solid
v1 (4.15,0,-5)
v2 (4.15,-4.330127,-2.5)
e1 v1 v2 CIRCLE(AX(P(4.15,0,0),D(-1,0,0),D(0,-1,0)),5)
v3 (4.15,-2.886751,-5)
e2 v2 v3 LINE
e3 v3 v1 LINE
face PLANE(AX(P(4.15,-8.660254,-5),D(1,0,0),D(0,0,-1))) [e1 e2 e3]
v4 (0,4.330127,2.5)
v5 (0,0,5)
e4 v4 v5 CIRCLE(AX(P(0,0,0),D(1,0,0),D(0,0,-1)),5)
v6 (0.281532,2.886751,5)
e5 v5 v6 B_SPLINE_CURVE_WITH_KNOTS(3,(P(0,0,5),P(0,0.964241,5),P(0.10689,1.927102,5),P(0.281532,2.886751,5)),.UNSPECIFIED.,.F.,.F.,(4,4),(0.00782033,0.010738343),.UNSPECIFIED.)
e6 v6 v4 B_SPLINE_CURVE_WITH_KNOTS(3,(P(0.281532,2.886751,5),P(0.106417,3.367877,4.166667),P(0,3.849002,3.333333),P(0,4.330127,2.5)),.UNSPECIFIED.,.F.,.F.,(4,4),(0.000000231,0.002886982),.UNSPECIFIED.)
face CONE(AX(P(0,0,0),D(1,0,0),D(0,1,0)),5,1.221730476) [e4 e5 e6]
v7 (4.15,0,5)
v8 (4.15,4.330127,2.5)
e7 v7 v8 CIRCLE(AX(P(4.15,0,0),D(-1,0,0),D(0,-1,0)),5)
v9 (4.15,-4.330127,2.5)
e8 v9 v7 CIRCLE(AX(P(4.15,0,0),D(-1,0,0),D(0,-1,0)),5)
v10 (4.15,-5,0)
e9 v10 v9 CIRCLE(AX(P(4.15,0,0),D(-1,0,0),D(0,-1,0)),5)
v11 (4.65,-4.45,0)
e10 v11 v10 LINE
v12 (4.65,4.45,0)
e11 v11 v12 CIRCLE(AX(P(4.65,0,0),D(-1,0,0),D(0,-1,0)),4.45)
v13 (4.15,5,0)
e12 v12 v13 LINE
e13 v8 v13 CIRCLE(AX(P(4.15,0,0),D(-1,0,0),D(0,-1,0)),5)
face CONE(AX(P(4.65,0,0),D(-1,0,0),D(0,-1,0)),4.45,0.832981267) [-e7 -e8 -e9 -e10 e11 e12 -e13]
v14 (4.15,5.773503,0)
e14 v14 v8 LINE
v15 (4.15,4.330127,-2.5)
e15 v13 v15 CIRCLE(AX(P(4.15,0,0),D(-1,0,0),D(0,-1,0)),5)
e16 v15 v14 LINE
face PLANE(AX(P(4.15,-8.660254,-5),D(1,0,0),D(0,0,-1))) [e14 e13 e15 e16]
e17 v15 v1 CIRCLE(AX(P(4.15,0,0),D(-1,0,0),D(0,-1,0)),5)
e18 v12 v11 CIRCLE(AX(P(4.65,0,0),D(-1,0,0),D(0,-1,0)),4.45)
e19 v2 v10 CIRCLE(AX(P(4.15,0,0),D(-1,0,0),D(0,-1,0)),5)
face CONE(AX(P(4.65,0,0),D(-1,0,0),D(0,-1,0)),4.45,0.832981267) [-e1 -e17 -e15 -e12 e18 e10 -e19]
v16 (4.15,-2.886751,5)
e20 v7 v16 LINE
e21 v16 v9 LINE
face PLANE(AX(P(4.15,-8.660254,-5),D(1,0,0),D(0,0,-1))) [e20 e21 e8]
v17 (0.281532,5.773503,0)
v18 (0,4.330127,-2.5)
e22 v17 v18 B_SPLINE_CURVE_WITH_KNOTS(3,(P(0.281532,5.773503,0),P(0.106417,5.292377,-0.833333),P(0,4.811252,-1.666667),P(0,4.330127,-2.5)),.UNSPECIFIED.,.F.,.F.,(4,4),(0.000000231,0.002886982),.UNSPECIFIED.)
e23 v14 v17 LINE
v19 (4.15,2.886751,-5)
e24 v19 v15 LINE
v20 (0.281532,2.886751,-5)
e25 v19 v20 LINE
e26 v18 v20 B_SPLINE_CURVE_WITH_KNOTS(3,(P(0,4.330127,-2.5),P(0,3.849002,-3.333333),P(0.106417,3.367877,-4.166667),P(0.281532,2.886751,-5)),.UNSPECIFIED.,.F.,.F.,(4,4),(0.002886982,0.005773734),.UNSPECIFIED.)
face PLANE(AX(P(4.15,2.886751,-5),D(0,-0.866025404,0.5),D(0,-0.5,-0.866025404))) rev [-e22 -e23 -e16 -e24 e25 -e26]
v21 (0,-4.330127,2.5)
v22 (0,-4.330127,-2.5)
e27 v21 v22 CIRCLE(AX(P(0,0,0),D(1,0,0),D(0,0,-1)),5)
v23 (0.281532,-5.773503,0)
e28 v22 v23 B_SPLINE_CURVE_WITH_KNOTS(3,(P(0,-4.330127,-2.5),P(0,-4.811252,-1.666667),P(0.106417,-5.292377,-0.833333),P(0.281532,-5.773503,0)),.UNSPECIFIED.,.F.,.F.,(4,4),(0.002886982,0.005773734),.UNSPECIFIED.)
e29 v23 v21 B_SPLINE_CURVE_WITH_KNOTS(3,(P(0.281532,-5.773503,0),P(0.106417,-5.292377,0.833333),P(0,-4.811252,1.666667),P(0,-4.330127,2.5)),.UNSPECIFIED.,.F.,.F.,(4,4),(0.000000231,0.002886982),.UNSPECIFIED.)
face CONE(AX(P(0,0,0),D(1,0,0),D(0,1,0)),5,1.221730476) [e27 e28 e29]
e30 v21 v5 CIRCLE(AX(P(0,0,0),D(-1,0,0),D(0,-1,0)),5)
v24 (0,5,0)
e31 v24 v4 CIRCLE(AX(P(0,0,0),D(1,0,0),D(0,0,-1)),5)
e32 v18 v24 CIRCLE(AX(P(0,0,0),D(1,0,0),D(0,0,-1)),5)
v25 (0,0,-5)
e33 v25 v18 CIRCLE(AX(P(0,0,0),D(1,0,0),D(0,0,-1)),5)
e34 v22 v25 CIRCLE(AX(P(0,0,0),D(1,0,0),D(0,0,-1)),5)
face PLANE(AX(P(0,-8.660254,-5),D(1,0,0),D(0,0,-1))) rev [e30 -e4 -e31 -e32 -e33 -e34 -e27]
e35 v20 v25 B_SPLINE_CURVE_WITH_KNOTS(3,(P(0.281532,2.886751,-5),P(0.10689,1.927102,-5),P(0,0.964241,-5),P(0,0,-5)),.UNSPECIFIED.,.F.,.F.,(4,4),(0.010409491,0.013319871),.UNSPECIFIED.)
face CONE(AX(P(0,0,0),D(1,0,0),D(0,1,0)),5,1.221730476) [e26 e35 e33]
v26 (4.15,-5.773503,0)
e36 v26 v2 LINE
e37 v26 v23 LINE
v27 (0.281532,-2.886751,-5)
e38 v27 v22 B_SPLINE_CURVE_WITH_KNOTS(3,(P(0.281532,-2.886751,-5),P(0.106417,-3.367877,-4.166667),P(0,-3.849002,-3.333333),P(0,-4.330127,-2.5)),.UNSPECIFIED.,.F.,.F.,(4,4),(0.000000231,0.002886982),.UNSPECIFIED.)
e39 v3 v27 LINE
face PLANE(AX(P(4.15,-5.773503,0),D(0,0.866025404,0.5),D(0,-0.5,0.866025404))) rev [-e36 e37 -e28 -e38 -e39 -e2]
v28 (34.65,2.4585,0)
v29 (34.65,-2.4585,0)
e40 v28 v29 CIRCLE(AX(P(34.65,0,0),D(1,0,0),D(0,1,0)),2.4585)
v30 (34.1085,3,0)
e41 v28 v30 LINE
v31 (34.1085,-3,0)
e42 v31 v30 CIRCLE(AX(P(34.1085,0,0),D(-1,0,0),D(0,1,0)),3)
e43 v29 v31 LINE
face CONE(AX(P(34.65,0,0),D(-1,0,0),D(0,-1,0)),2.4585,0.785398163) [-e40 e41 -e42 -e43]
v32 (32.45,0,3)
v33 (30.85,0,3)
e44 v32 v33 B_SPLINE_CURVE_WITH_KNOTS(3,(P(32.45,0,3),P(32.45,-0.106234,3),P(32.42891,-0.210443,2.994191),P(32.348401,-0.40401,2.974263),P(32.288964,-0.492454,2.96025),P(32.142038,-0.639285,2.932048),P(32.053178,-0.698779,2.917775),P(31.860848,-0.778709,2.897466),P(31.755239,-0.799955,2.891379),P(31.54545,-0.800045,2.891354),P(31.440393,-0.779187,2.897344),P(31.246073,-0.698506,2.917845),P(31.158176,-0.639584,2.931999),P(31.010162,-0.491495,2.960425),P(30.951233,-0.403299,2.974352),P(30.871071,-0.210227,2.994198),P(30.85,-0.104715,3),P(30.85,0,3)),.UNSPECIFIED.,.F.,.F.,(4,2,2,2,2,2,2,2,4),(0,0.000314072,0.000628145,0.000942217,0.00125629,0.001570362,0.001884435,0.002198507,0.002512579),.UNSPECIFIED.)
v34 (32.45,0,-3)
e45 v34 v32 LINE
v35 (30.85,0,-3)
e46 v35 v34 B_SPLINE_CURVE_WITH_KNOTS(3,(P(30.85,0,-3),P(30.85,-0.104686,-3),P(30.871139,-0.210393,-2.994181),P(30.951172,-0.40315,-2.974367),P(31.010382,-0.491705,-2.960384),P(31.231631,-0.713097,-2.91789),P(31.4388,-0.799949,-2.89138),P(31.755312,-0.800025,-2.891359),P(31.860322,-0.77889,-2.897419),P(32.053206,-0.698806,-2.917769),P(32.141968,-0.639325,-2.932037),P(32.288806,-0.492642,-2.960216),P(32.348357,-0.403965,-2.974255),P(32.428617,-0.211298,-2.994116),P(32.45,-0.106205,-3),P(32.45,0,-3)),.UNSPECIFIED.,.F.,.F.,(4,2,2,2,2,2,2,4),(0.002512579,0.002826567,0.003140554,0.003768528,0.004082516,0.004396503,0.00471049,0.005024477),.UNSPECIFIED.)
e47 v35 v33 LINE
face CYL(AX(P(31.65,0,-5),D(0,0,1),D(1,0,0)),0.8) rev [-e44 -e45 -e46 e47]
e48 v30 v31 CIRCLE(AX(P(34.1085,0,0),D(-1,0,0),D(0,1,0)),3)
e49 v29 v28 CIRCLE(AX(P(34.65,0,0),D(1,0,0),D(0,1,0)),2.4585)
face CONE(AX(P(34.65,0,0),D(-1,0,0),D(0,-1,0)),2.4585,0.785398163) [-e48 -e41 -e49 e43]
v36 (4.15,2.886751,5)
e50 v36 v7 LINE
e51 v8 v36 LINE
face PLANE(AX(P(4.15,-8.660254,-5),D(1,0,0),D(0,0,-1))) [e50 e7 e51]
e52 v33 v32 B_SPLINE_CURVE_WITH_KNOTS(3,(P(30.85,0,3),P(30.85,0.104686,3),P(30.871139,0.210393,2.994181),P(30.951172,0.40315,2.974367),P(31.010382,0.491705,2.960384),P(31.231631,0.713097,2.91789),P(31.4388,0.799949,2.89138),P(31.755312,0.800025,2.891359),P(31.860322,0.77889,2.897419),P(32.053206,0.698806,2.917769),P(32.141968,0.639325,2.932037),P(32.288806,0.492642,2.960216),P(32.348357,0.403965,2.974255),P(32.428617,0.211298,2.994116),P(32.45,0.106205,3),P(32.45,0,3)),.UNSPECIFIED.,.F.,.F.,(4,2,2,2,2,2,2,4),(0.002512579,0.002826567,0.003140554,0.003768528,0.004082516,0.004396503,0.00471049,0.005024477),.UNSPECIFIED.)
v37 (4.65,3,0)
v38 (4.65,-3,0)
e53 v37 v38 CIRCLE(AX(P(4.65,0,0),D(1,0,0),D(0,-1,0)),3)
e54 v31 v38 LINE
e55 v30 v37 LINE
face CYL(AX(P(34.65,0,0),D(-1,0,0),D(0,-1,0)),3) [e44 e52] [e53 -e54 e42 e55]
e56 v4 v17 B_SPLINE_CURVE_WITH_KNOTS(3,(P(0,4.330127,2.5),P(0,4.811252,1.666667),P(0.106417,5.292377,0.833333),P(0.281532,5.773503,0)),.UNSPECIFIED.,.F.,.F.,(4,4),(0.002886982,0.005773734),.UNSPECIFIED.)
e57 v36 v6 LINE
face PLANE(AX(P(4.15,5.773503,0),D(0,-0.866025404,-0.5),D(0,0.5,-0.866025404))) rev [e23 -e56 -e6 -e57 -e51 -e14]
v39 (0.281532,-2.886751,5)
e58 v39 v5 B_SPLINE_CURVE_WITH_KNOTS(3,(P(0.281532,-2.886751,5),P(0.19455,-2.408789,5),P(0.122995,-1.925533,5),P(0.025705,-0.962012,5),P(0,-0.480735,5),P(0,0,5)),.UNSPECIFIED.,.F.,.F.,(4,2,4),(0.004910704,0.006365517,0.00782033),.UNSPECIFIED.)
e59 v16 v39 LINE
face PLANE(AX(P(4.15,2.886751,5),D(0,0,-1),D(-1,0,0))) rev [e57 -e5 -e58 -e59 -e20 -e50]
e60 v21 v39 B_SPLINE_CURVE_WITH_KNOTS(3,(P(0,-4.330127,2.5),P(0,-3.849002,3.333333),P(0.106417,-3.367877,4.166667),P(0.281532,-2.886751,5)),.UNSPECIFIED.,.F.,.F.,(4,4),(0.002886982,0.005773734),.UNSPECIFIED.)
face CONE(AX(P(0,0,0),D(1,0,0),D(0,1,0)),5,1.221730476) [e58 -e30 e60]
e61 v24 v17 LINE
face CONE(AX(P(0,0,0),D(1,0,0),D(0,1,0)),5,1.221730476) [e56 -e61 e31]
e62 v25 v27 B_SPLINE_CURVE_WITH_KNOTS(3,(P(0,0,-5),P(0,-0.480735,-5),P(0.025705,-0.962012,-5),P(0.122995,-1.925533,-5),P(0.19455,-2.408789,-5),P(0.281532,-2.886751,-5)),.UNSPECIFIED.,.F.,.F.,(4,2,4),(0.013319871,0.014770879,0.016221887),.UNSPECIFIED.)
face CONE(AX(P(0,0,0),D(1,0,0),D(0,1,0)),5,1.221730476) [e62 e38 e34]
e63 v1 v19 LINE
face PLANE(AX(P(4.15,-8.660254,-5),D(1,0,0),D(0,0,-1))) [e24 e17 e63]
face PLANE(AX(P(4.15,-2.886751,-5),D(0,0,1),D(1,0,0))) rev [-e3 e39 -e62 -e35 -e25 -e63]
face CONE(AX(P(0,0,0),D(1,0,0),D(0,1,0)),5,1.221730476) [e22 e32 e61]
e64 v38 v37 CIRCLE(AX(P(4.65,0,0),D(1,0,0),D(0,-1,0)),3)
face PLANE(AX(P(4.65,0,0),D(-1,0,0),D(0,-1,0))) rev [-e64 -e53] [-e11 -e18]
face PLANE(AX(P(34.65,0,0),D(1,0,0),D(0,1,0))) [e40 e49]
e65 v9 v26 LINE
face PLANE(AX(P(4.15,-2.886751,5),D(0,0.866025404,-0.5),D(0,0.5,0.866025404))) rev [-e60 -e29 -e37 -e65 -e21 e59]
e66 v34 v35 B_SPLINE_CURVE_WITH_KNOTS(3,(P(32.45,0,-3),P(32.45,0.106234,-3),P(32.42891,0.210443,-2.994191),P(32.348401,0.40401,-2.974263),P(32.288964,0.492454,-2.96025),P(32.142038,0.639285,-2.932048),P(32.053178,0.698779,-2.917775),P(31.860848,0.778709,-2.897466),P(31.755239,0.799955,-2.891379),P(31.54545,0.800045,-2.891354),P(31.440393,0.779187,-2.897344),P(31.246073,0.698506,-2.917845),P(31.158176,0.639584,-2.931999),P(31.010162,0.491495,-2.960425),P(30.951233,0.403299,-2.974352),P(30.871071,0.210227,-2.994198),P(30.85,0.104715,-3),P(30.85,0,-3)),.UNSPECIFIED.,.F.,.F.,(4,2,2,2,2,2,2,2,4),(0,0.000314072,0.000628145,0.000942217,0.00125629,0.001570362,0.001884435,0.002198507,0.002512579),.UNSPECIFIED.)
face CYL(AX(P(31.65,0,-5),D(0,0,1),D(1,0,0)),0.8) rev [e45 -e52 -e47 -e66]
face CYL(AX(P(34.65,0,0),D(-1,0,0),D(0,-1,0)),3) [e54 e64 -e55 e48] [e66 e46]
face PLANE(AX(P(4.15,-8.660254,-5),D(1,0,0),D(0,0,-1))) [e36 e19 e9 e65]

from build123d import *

# Parameters (mm, degrees)
BASEHEAD_DEPTH  = 4.15
SKETCH3_R       = 3
BASEBODY_DEPTH  = 30
CHAMFER1_SIZE   = 0.5415
HOLE_DEPTH      = 36.481767619
HOLE_DEPTH_BACK = 36.481767619
SKETCH5_R       = 0.8


with BuildPart() as part:
    # Sketch-BaseHead → BaseHead (new body)
    with BuildSketch(Plane(origin=(0, 0, 0), x_dir=(0, 0, -1), z_dir=(1, 0, 0))):
        Polygon((0, -5.773502692), (5, -2.886751346), (5, 2.886751346), (0, 5.773502692), (-5, 2.886751346), (-5, -2.886751346), align=None)
    extrude(amount=BASEHEAD_DEPTH)

    # Sketch4 → HeadChamfer (revolve, cut)
    with BuildSketch(Plane(origin=(-0.264637255, -5.916896391, 0), x_dir=(0, 1, 0), z_dir=(0, 0, 1))):
        Polygon((11.690399083, -0.264637255), (10.916896391, -0.264637255), (11.690399083, -0.546169211), align=None)
    revolve(axis=Axis((-4.001564945, 0, 0), (1, 0, 0)), mode=Mode.SUBTRACT)

    # Sketch1 → Revolve1 (revolve)
    with BuildSketch(Plane(origin=(0, 0, 0), x_dir=(1, 0, 0), z_dir=(0, 1, 0)), mode=Mode.PRIVATE) as revolve1_sk:
        Polygon((4.15, 0), (4.65, 0), (4.65, 4.45), (4.15, 5), align=None)
    revolve(revolve1_sk.sketch.rotate(Axis((-4.001564945, 0, 0), (1, 0, 0)), 270), axis=Axis((-4.001564945, 0, 0), (1, 0, 0)))

    # Sketch3 → BaseBody (add)
    with BuildSketch(Plane(origin=(4.65, 0, 0), x_dir=(0, 0, -1), z_dir=(1, 0, 0))):
        with Locations(Location((0, 0, 0), (0, 0, 270))):
            Circle(SKETCH3_R)
    extrude(amount=BASEBODY_DEPTH)

    # Chamfer1
    chamfer1_edges = [part.edges().sort_by_distance(p)[0] for p in [
        (34.65, 3, 0),
    ]]
    chamfer(chamfer1_edges, length=CHAMFER1_SIZE)

    # Sketch5 → Hole (cut, two sides: drawn at the far end of the back side and taken through both)
    with BuildSketch(Plane.XY.offset(-HOLE_DEPTH_BACK)):
        with Locations((31.65, 0)):
            Circle(SKETCH5_R)
    extrude(amount=HOLE_DEPTH + HOLE_DEPTH_BACK, mode=Mode.SUBTRACT)


solid = part.part
